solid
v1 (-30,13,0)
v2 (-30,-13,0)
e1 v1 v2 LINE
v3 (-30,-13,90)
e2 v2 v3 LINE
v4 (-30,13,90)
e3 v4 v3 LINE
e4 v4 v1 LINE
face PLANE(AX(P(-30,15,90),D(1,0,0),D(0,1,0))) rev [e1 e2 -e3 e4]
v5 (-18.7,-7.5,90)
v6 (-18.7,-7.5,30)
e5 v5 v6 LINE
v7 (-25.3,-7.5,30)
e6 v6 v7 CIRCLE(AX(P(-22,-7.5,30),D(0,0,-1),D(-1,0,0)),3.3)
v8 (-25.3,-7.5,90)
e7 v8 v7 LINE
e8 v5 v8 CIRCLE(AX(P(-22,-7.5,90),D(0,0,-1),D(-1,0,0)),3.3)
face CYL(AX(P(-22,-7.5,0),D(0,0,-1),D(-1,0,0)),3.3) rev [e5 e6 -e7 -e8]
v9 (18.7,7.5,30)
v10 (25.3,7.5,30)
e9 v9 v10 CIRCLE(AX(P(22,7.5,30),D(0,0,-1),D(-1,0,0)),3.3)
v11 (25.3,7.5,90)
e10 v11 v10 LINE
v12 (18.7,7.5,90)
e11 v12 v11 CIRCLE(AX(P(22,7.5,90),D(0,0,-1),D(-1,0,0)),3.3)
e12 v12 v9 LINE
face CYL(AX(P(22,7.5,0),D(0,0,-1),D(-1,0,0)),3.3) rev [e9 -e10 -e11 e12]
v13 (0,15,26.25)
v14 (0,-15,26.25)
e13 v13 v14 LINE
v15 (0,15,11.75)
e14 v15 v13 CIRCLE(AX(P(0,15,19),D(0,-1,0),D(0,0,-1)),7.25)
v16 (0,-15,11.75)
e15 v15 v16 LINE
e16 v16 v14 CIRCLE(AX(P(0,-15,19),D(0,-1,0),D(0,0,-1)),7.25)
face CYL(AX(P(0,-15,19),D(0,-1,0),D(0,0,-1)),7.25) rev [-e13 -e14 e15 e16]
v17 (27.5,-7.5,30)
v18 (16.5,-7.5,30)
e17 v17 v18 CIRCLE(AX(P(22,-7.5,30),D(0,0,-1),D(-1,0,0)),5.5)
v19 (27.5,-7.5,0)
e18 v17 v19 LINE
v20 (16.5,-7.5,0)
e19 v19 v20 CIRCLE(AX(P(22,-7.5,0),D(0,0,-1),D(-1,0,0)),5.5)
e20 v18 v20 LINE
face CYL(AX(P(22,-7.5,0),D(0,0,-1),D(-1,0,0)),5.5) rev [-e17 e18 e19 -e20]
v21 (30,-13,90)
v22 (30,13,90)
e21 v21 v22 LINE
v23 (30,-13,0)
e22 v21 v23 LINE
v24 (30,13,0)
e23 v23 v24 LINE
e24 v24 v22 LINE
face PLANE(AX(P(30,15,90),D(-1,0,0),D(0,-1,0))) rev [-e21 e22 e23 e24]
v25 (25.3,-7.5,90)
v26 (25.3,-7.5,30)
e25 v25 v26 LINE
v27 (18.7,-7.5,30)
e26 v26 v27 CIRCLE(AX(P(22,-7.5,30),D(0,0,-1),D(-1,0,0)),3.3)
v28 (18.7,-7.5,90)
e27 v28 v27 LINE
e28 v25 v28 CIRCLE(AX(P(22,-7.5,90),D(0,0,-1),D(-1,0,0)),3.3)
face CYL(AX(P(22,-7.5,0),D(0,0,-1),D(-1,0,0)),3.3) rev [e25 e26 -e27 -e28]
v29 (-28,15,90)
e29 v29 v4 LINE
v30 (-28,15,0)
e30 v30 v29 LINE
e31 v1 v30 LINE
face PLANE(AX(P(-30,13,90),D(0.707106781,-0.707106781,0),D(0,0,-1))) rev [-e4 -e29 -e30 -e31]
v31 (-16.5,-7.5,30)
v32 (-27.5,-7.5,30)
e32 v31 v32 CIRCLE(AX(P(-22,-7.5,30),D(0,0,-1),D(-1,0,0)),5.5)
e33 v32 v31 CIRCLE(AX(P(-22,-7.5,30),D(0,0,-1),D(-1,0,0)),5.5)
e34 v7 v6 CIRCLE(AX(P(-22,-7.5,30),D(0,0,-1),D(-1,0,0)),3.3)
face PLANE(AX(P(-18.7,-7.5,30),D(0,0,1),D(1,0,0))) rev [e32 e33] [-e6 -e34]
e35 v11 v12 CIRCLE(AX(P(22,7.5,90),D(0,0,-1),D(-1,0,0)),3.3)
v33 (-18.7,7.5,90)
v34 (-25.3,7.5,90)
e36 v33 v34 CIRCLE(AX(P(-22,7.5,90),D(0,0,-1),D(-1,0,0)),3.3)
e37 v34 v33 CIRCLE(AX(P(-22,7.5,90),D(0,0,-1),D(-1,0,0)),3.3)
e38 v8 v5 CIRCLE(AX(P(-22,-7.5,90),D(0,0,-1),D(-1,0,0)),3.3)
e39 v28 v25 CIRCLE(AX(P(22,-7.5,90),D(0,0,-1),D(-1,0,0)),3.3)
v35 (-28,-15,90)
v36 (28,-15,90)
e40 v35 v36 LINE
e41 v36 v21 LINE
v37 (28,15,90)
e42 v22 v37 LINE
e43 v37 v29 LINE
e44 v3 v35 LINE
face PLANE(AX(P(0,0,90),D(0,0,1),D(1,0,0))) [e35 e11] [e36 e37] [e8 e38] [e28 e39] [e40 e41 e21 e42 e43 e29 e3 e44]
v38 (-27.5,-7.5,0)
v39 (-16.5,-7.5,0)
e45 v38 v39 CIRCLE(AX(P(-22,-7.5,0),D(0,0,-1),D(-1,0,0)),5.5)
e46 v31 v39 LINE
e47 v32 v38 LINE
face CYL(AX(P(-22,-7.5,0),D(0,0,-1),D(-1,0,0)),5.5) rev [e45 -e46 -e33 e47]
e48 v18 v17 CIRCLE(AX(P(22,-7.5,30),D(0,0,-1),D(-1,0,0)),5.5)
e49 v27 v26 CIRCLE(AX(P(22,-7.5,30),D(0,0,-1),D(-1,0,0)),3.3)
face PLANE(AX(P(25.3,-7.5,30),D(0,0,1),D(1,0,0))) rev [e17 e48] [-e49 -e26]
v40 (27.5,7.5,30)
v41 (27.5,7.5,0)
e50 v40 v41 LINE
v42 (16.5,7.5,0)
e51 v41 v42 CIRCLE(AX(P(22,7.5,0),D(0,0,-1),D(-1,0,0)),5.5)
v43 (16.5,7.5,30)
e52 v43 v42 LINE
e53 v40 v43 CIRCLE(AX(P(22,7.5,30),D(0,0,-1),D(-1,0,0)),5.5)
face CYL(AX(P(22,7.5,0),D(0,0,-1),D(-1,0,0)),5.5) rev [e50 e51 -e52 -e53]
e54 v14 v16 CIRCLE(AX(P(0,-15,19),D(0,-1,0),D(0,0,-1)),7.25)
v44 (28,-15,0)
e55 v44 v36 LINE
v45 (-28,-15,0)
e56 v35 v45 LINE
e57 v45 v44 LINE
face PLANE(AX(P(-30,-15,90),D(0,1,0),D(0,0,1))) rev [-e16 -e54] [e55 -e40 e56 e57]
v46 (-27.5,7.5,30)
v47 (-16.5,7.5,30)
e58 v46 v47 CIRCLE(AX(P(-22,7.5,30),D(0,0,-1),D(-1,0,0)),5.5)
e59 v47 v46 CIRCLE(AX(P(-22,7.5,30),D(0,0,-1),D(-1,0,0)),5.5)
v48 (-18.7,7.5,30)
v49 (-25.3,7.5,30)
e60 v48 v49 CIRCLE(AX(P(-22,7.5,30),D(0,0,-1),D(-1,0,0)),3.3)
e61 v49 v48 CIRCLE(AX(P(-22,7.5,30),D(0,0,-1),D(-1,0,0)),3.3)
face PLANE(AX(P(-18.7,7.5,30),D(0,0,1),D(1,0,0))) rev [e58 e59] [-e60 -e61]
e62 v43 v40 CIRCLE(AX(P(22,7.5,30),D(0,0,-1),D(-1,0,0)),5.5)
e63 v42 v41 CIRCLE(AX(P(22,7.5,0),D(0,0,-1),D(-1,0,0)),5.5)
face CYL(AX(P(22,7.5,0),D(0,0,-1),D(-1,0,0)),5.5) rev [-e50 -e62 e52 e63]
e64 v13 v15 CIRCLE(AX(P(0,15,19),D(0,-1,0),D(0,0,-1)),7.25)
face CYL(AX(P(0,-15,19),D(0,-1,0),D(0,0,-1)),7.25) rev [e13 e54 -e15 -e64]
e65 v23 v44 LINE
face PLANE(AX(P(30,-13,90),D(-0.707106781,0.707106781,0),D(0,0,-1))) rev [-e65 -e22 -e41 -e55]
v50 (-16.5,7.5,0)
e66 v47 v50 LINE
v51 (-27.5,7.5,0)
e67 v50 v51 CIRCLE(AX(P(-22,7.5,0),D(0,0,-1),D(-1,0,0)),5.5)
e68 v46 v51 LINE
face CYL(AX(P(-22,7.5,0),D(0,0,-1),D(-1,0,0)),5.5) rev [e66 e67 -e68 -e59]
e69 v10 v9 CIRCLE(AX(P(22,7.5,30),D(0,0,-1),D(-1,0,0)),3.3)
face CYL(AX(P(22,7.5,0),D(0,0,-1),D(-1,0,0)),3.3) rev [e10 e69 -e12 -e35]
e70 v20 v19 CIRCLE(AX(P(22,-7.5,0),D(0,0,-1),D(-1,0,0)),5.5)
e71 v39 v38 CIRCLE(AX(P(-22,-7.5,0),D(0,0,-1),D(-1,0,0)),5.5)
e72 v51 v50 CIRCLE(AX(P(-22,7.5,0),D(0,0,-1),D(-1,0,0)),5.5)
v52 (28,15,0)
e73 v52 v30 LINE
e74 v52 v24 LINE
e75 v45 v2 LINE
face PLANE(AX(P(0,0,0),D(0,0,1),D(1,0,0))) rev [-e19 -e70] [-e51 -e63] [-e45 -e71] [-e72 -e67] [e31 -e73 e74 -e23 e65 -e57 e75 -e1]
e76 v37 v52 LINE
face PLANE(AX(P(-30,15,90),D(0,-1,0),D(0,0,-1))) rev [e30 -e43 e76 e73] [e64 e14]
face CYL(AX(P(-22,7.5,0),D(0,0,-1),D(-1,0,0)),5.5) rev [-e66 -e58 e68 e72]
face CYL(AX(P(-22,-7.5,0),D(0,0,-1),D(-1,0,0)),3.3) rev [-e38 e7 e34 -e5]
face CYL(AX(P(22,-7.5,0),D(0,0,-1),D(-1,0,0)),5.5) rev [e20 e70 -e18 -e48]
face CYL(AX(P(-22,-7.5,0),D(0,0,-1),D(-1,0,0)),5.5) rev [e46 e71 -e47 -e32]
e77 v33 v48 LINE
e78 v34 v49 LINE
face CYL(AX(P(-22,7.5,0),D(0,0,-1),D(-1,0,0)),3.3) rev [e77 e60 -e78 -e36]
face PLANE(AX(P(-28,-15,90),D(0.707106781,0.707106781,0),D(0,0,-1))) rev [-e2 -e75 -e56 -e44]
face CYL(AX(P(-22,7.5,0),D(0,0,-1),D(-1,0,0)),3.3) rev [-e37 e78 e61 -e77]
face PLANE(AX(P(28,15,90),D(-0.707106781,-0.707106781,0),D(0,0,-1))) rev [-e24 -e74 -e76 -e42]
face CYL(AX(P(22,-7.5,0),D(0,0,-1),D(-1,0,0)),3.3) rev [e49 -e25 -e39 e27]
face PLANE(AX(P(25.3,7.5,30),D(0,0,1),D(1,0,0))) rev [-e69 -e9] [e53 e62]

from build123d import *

# Parameters (mm, degrees)
SKETCH_1_W                   = 60
SKETCH_1_H                   = 30
EXTRUDE_1_DEPTH              = 90
M16X1_5_1_D                  = 14.5
HOLE_WIZARD_M6_1_D           = 6.6
HOLE_WIZARD_M6_1_CBORE_D     = 11
HOLE_WIZARD_M6_1_CBORE_DEPTH = 30
CHAMFER_1_SIZE               = 2


with BuildPart() as part:
    # 草图1 → 凸台-拉伸1 (new body)
    with BuildSketch(Plane.XY):
        Rectangle(SKETCH_1_W, SKETCH_1_H)
    extrude(amount=EXTRUDE_1_DEPTH)

    # M16x1.5 螺纹孔1 (through all)
    with Locations(Plane(origin=(0, -15, 0), x_dir=(-1, 0, 0), z_dir=(0, -1, 0))):
        with Locations((0, -19)):
            Hole(M16X1_5_1_D / 2)

    # M6 六角凹头螺钉的柱形沉头孔1 (through all)
    with Locations(Plane(origin=(0, 0, 0), x_dir=(-1, 0, 0), z_dir=(0, 0, -1))):
        with Locations((22, -7.5), (22, 7.5), (-22, 7.5), (-22, -7.5)):
            CounterBoreHole(HOLE_WIZARD_M6_1_D / 2, HOLE_WIZARD_M6_1_CBORE_D / 2, HOLE_WIZARD_M6_1_CBORE_DEPTH)

    # 倒角1
    chamfer_1_edges = [part.edges().sort_by_distance(p)[0] for p in [
        (30, -15, 45),
        (-30, -15, 45),
        (-30, 15, 45),
        (30, 15, 45),
    ]]
    chamfer(chamfer_1_edges, length=CHAMFER_1_SIZE)


solid = part.part
